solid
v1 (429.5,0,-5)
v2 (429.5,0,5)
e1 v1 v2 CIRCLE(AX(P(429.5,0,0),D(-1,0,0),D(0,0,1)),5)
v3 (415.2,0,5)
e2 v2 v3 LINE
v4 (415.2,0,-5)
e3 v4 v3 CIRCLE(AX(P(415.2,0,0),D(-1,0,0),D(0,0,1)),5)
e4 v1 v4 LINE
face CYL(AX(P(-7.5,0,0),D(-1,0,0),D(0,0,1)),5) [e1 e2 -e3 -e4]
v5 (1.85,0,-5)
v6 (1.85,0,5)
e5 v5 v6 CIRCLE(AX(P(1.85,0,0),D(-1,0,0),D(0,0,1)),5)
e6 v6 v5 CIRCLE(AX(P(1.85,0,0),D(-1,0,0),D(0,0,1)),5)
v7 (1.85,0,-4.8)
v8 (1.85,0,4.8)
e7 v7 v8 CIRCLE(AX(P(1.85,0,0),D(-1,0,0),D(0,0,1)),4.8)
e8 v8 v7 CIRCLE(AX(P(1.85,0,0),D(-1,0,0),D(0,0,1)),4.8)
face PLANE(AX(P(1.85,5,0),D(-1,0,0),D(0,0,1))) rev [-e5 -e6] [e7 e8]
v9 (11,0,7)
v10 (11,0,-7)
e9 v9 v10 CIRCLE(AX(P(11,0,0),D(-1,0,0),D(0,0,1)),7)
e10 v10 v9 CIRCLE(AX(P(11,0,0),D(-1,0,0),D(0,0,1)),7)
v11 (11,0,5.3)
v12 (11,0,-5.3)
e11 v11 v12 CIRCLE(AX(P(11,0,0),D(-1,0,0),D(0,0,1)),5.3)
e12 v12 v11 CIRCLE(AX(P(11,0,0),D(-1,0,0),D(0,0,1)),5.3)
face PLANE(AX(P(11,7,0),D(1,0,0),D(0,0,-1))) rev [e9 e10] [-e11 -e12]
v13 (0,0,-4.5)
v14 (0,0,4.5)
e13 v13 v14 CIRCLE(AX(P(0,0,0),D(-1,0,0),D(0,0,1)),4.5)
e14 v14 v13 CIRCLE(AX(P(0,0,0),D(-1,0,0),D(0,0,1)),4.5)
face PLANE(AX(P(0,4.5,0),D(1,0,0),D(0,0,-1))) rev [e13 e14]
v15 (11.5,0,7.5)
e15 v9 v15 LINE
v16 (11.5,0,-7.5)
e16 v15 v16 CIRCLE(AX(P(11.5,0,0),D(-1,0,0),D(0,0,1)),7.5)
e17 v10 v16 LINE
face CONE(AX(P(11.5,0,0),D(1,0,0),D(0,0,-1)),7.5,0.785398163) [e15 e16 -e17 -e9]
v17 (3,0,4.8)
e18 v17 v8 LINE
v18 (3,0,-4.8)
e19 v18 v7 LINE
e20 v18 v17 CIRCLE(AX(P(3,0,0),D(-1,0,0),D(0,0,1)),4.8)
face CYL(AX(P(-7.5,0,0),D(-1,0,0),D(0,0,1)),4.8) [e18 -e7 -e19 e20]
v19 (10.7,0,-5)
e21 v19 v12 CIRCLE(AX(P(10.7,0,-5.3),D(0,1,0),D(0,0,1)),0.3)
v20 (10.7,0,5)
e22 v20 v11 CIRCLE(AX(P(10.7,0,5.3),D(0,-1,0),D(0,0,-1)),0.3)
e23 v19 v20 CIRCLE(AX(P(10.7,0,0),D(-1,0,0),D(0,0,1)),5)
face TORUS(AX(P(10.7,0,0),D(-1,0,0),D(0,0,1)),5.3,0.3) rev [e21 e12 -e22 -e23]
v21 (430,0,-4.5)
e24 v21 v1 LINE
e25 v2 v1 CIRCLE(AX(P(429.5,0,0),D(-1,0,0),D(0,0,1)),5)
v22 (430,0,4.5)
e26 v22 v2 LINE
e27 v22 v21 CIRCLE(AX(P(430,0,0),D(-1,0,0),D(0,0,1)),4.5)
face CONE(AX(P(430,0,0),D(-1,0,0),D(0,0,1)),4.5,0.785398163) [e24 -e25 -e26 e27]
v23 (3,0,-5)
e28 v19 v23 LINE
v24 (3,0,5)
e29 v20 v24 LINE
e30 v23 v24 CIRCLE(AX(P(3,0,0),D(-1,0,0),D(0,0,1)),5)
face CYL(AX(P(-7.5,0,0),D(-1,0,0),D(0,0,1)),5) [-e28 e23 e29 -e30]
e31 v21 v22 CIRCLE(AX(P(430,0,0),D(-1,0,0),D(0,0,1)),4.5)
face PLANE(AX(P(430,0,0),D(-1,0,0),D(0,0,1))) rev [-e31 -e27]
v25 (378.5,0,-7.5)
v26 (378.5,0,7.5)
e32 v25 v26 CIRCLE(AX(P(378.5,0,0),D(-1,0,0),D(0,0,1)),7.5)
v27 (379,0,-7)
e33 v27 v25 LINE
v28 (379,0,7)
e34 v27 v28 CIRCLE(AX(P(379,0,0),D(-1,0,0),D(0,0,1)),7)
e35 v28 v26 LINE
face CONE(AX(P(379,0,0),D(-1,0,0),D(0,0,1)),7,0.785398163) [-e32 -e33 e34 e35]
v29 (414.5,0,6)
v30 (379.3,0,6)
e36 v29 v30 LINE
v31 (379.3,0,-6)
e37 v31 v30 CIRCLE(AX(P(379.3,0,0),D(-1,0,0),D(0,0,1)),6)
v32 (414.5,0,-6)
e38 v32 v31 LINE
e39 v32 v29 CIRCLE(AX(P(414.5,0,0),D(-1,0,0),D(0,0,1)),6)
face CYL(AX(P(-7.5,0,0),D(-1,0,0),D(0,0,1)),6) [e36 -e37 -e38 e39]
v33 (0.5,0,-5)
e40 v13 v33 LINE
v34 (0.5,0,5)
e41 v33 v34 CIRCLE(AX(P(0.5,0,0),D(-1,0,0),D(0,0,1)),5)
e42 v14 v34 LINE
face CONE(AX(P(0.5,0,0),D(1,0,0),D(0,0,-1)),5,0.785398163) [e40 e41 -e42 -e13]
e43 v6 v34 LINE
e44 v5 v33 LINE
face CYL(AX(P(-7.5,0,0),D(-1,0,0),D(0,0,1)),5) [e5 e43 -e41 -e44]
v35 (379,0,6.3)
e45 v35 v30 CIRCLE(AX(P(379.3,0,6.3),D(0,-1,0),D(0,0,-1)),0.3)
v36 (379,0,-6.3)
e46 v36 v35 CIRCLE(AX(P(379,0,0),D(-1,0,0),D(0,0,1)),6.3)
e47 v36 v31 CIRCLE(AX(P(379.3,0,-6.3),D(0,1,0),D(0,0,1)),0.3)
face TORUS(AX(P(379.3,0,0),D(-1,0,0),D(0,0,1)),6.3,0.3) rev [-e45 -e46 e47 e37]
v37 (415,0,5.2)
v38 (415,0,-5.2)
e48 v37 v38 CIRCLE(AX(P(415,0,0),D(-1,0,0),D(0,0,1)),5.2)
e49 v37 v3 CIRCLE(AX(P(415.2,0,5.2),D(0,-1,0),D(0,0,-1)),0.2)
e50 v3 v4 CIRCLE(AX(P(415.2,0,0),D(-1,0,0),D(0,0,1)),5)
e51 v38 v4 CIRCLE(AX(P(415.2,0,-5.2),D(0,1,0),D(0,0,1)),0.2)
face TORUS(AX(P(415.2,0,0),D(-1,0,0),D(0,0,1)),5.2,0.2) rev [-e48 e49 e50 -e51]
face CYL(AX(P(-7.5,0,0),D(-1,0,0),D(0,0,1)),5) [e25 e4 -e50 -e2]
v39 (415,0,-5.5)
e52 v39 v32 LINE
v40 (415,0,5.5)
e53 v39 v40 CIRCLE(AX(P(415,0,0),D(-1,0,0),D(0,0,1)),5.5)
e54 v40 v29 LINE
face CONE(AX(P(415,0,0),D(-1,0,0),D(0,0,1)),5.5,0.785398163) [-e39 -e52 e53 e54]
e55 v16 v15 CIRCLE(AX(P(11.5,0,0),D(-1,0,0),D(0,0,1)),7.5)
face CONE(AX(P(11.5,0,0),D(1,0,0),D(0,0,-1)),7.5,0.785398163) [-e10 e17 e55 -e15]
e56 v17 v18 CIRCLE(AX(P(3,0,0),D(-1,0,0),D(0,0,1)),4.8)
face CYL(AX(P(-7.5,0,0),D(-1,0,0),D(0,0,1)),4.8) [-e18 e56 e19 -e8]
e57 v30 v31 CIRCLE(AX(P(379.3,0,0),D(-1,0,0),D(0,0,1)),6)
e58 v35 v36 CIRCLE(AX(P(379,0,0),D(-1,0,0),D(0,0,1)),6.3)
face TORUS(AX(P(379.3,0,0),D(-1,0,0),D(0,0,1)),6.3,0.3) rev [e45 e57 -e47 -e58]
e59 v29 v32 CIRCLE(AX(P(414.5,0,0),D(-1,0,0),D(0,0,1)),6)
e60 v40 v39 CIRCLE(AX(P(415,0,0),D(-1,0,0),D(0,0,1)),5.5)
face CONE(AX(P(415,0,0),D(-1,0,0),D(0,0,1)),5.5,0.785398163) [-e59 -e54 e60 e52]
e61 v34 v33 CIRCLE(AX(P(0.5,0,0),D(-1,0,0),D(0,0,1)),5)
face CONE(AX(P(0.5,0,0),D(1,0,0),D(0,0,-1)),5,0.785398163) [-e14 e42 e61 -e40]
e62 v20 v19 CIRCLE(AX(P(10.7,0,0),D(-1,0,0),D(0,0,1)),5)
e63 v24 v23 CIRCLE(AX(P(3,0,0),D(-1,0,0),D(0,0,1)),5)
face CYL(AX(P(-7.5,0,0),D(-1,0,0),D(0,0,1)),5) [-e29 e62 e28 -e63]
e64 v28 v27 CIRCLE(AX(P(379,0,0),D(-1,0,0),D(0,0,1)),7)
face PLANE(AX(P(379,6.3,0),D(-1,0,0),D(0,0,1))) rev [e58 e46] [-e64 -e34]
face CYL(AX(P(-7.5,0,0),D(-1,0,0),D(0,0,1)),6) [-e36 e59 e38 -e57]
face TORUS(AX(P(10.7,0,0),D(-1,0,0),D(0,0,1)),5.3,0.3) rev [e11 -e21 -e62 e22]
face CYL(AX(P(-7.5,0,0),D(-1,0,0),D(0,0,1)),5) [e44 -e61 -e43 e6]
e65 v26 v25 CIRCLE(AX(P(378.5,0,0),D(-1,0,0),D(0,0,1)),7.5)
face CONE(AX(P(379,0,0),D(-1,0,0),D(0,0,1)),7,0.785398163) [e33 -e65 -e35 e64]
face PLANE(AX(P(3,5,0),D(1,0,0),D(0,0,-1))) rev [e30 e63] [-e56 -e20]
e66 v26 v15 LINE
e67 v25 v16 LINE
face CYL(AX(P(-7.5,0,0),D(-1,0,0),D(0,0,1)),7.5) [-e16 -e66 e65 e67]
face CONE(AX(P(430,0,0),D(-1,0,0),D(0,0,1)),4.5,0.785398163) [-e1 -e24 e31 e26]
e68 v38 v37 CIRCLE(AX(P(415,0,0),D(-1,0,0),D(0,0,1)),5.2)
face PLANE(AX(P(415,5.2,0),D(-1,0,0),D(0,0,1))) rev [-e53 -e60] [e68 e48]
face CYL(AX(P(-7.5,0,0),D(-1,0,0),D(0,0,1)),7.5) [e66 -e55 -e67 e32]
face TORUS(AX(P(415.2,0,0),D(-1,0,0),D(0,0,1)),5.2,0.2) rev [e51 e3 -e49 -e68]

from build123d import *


with BuildPart() as part:
    # Sketch1 → Revolve1 (revolve)
    with BuildSketch(Plane.XY, mode=Mode.PRIVATE) as revolve1_sk:
        with BuildLine():
            Line((1.85, 5), (1.85, 4.8))
            Line((1.85, 4.8), (3, 4.8))
            Line((3, 4.8), (3, 5))
            Line((3, 5), (10.7, 5))
            ThreePointArc((10.7, 5), (10.912132034, 5.087867966), (11, 5.3))
            Line((11, 5.3), (11, 7))
            Line((11, 7), (11.5, 7.5))
            Line((11.5, 7.5), (378.5, 7.5))
            Line((378.5, 7.5), (379, 7))
            Line((379, 7), (379, 6.3))
            ThreePointArc((379, 6.3), (379.087867966, 6.087867966), (379.3, 6))
            Line((379.3, 6), (414.5, 6))
            Line((414.5, 6), (415, 5.5))
            Line((415, 5.5), (415, 5.2))
            ThreePointArc((415, 5.2), (415.058578644, 5.058578644), (415.2, 5))
            Line((415.2, 5), (429.5, 5))
            Line((429.5, 5), (430, 4.5))
            Line((430, 4.5), (430, 0))
            Line((430, 0), (0, 0))
            Line((0, 0), (0, 4.5))
            Line((0, 4.5), (0.5, 5))
            Line((0.5, 5), (1.85, 5))
        make_face()
    revolve(revolve1_sk.sketch.rotate(Axis((-7.5, 0, 0), (1, 0, 0)), 90), axis=Axis((-7.5, 0, 0), (1, 0, 0)))


solid = part.part
